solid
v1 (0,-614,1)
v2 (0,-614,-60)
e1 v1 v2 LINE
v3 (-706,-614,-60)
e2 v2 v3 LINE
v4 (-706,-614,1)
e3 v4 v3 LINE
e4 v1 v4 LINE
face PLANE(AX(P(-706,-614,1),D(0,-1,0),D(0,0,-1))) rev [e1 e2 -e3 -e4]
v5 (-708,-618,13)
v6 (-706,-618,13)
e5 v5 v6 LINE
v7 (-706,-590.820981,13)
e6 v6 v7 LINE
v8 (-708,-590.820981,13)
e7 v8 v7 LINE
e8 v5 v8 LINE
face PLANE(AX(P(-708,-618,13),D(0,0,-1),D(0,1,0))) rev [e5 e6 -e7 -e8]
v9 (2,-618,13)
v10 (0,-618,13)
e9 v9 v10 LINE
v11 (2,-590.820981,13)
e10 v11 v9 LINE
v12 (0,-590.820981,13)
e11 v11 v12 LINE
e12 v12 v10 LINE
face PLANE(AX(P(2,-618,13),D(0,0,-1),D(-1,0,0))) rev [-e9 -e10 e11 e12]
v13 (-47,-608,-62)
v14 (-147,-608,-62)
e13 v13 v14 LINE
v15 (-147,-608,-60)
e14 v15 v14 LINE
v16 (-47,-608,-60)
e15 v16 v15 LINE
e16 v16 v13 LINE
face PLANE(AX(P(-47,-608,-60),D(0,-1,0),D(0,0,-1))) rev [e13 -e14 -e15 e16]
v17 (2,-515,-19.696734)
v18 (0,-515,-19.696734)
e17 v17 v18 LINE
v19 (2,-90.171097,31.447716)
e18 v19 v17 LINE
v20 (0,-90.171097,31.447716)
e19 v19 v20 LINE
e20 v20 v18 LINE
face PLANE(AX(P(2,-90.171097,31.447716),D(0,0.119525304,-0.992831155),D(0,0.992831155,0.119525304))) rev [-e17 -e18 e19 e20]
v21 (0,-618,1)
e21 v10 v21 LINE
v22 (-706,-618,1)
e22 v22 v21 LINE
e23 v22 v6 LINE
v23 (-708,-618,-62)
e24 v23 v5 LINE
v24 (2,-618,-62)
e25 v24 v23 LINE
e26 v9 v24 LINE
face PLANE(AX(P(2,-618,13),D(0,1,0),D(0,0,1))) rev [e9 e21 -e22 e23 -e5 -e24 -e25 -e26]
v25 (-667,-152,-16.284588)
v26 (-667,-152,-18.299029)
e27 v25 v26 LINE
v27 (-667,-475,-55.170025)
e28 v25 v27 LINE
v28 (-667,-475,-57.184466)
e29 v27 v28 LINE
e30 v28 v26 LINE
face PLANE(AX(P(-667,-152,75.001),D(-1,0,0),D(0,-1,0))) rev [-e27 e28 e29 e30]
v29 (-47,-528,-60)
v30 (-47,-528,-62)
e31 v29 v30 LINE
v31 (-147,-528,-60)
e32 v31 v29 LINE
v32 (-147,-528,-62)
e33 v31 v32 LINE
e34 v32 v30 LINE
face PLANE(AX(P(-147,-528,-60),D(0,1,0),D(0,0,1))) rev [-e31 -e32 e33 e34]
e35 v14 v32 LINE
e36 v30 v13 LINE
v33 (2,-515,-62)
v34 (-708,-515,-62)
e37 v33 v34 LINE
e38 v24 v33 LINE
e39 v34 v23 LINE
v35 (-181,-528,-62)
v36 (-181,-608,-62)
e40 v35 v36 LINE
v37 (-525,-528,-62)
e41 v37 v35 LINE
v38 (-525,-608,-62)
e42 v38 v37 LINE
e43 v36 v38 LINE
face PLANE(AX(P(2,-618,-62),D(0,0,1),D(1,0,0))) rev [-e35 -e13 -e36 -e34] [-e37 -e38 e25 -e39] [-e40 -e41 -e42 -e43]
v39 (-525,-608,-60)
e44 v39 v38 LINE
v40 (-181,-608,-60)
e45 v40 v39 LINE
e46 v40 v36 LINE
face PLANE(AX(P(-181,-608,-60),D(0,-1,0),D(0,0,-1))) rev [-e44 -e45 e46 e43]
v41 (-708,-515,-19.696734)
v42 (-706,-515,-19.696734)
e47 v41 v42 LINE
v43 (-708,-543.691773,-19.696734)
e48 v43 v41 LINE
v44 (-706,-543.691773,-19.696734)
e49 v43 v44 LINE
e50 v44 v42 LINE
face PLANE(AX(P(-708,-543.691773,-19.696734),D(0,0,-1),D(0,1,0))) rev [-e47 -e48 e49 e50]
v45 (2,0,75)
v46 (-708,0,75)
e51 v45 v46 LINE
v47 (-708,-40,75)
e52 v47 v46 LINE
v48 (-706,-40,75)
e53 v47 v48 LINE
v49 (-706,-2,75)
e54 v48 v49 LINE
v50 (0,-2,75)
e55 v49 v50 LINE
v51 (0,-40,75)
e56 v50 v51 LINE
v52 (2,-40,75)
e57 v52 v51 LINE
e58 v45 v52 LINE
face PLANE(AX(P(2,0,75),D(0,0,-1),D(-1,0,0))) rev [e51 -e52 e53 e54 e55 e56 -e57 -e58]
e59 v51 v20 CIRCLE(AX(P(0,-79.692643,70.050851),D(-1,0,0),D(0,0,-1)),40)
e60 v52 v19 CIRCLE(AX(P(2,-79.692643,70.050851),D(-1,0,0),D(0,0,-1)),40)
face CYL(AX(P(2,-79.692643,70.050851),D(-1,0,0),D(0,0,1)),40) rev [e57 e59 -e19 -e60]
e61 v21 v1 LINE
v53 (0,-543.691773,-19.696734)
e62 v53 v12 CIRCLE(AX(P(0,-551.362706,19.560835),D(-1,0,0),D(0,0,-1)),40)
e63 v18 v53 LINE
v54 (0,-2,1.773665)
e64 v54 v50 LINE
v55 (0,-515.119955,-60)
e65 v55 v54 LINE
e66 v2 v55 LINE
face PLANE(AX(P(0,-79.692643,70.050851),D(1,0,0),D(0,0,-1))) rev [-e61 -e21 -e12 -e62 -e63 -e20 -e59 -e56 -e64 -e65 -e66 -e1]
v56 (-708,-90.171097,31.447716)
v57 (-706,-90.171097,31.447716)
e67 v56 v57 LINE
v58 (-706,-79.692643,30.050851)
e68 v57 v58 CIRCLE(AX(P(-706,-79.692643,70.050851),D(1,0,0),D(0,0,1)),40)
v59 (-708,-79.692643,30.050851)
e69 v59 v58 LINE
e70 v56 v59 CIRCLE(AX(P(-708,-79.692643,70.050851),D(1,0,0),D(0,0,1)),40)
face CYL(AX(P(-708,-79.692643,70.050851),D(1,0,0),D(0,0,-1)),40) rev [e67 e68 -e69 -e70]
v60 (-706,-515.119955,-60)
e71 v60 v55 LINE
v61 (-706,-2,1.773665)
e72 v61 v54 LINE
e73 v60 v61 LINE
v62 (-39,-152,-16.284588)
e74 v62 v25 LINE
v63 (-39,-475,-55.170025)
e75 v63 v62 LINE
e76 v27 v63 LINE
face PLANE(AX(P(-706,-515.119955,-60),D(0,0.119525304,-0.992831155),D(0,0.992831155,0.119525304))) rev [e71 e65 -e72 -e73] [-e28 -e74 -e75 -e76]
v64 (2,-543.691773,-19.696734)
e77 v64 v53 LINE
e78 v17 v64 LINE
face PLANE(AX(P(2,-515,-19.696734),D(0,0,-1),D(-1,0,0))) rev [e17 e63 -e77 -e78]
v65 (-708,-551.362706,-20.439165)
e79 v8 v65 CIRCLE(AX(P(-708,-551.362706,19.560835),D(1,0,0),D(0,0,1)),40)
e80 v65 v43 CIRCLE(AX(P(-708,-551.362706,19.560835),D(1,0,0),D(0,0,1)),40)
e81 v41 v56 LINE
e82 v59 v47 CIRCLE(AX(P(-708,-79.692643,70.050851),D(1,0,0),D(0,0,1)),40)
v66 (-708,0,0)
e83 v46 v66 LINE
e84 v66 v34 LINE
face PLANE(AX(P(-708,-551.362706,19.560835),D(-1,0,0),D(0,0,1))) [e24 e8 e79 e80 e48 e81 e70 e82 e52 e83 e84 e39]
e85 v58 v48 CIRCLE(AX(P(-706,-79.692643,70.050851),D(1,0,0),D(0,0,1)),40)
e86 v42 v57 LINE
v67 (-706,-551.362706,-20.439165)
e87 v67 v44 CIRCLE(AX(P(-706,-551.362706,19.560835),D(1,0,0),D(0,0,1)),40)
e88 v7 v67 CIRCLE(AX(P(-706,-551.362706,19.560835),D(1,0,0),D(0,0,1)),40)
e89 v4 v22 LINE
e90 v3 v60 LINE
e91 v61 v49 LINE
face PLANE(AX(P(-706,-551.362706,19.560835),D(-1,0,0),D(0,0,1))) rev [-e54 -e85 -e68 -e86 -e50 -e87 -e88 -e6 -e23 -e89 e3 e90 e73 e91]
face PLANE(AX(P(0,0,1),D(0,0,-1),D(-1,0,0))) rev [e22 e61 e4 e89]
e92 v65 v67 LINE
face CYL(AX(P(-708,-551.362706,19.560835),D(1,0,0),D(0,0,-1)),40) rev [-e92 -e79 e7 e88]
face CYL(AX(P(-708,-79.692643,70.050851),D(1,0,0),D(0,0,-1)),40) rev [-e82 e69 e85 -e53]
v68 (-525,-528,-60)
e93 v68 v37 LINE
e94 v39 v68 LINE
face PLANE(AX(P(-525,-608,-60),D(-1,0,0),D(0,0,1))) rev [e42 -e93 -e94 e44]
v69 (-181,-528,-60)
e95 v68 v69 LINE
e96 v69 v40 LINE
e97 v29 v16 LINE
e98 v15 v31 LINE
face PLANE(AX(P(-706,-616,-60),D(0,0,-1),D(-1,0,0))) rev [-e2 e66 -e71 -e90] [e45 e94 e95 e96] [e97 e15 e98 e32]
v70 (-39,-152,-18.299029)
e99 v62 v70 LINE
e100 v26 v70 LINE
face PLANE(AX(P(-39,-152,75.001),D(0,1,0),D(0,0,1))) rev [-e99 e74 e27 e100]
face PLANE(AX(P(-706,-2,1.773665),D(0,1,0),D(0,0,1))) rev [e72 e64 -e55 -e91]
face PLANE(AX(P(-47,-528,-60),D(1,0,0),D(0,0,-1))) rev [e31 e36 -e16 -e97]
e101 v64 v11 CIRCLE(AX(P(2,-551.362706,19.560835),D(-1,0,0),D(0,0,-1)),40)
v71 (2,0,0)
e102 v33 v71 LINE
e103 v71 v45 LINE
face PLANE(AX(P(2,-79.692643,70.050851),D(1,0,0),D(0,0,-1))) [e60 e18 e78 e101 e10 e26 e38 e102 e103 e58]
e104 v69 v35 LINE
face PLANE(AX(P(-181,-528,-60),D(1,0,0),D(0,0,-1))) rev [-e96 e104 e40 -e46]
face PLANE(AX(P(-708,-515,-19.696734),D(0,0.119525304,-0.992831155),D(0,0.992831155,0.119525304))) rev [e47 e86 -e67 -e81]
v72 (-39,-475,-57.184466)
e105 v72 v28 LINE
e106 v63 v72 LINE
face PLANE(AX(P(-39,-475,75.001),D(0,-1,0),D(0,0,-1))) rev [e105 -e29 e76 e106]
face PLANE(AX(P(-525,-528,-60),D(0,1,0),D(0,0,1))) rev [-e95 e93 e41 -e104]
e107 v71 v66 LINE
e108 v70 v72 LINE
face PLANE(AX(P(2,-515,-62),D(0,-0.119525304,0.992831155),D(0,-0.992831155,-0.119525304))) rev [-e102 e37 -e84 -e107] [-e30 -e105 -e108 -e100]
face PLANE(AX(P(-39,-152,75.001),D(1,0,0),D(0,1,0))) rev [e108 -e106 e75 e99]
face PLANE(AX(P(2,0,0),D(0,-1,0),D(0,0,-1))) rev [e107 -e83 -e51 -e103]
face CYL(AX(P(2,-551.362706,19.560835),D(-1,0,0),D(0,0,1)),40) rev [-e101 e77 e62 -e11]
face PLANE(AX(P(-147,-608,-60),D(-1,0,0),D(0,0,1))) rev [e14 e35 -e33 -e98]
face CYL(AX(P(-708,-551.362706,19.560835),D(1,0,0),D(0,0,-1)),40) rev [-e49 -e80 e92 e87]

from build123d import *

# Parameters (mm, degrees)
BOSS_EXTRUDE1_DEPTH = 2
BOSS_EXTRUDE2_DEPTH = 706
SKETCH3_W           = 706
SKETCH3_H           = 73
CUT_EXTRUDE1_DEPTH  = 940.955850027
BOSS_EXTRUDE3_START = 2
BOSS_EXTRUDE3_DEPTH = 2
CUT_EXTRUDE2_REACH  = 951.714
SKETCH5_W           = 628
SKETCH5_H           = 323
SKETCH6_W           = 100
SKETCH6_H           = 80
SKETCH6_W_2         = 344
CUT_EXTRUDE3_DEPTH  = 2
SKETCH7_W           = 706
SKETCH7_H           = 4
BOSS_EXTRUDE4_DEPTH = 61


with BuildPart() as part:
    # Sketch1 → Boss-Extrude1 (new body)
    with BuildSketch(Plane(origin=(0, 0, 0), x_dir=(0, 0, -1), z_dir=(1, 0, 0))):
        with BuildLine():
            Line((0, 0), (-75, 0))
            Line((-75, 0), (-75, -40))
            ThreePointArc((-75, -40), (-39.844354311, -53.471133381), (-31.447716035, -90.171096924))
            Line((-31.447716035, -90.171096924), (19.696734432, -515))
            Line((19.696734432, -515), (19.696734432, -543.691772505))
            ThreePointArc((19.696734432, -543.691772505), (13.304376378, -574.16353688), (-13, -590.820981133))
            Line((-13, -590.820981133), (-13, -618))
            Line((-13, -618), (62, -618))
            Line((62, -618), (62, -515))
            Line((62, -515), (0, 0))
        make_face()
    extrude(amount=BOSS_EXTRUDE1_DEPTH)

    # Sketch2 → Boss-Extrude2 (add)
    with BuildSketch(Plane.ZY):
        Polygon((13, -618), (-62, -618), (-62, -515), (0, 0), (75, 0), (75, -2), (1.773664518, -2), (-60, -515.119955274), (-60, -616), (13, -616), align=None)
    extrude(amount=BOSS_EXTRUDE2_DEPTH)

    # Sketch3 → Cut-Extrude1 (cut, through all)
    with BuildSketch(Plane(origin=(0, -616, 0), x_dir=(1, 0, 0), z_dir=(0, 1, 0))):
        with Locations((-353, 23.5)):
            Rectangle(SKETCH3_W, SKETCH3_H)
    extrude(amount=-CUT_EXTRUDE1_DEPTH, mode=Mode.SUBTRACT)

    # Sketch4 → Boss-Extrude3 (add)
    with BuildSketch(Plane.ZY.offset(706).offset(BOSS_EXTRUDE3_START)):
        with BuildLine():
            Line((-19.696734432, -543.691772505), (-19.696734432, -515))
            Line((-19.696734432, -515), (31.447716035, -90.171096924))
            ThreePointArc((31.447716035, -90.171096924), (39.844354311, -53.471133381), (75, -40))
            Line((75, -40), (75, 0))
            Line((75, 0), (0, 0))
            Line((0, 0), (-62, -515))
            Line((-62, -515), (-62, -618))
            Line((-62, -618), (13, -618))
            Line((13, -618), (13, -590.820981133))
            ThreePointArc((13, -590.820981133), (-13.304376378, -574.16353688), (-19.696734432, -543.691772505))
        make_face()
    extrude(amount=-BOSS_EXTRUDE3_DEPTH)

    # Cut-Extrude2: up to this plane
    cut_extrude2_end = Plane(origin=(-706, -515.119955274, -60), z_dir=(0, 0.1195253040577556, -0.9928311546732914))
    # Sketch5 → Cut-Extrude2 (cut, up to the surface)
    with BuildSketch(Plane(origin=(0, 0, -62), x_dir=(-1, 0, 0), z_dir=(0, 0, -1)), mode=Mode.PRIVATE) as cut_extrude2_sk1:
        with Locations((353, -313.5)):
            Rectangle(SKETCH5_W, SKETCH5_H)
    cut_extrude2_tool1 = split(extrude(cut_extrude2_sk1.sketch, amount=-CUT_EXTRUDE2_REACH, mode=Mode.PRIVATE), bisect_by=cut_extrude2_end, keep=Keep.BOTH, mode=Mode.PRIVATE)
    add(cut_extrude2_tool1.solids().sort_by_distance((-353, -313.5, -62))[0], mode=Mode.SUBTRACT)

    # Sketch6 → Cut-Extrude3 (cut)
    with BuildSketch(Plane(origin=(0, 0, -62), x_dir=(-1, 0, 0), z_dir=(0, 0, -1))):
        with Locations((97, -568)):
            Rectangle(SKETCH6_W, SKETCH6_H)
        with Locations((353, -568)):
            Rectangle(SKETCH6_W_2, SKETCH6_H)
    extrude(amount=-CUT_EXTRUDE3_DEPTH, mode=Mode.SUBTRACT)

    # Sketch7 → Boss-Extrude4 (add)
    with BuildSketch(Plane.XY.offset(-60)):
        with Locations((-353, -616)):
            Rectangle(SKETCH7_W, SKETCH7_H)
    extrude(amount=BOSS_EXTRUDE4_DEPTH)


solid = part.part
